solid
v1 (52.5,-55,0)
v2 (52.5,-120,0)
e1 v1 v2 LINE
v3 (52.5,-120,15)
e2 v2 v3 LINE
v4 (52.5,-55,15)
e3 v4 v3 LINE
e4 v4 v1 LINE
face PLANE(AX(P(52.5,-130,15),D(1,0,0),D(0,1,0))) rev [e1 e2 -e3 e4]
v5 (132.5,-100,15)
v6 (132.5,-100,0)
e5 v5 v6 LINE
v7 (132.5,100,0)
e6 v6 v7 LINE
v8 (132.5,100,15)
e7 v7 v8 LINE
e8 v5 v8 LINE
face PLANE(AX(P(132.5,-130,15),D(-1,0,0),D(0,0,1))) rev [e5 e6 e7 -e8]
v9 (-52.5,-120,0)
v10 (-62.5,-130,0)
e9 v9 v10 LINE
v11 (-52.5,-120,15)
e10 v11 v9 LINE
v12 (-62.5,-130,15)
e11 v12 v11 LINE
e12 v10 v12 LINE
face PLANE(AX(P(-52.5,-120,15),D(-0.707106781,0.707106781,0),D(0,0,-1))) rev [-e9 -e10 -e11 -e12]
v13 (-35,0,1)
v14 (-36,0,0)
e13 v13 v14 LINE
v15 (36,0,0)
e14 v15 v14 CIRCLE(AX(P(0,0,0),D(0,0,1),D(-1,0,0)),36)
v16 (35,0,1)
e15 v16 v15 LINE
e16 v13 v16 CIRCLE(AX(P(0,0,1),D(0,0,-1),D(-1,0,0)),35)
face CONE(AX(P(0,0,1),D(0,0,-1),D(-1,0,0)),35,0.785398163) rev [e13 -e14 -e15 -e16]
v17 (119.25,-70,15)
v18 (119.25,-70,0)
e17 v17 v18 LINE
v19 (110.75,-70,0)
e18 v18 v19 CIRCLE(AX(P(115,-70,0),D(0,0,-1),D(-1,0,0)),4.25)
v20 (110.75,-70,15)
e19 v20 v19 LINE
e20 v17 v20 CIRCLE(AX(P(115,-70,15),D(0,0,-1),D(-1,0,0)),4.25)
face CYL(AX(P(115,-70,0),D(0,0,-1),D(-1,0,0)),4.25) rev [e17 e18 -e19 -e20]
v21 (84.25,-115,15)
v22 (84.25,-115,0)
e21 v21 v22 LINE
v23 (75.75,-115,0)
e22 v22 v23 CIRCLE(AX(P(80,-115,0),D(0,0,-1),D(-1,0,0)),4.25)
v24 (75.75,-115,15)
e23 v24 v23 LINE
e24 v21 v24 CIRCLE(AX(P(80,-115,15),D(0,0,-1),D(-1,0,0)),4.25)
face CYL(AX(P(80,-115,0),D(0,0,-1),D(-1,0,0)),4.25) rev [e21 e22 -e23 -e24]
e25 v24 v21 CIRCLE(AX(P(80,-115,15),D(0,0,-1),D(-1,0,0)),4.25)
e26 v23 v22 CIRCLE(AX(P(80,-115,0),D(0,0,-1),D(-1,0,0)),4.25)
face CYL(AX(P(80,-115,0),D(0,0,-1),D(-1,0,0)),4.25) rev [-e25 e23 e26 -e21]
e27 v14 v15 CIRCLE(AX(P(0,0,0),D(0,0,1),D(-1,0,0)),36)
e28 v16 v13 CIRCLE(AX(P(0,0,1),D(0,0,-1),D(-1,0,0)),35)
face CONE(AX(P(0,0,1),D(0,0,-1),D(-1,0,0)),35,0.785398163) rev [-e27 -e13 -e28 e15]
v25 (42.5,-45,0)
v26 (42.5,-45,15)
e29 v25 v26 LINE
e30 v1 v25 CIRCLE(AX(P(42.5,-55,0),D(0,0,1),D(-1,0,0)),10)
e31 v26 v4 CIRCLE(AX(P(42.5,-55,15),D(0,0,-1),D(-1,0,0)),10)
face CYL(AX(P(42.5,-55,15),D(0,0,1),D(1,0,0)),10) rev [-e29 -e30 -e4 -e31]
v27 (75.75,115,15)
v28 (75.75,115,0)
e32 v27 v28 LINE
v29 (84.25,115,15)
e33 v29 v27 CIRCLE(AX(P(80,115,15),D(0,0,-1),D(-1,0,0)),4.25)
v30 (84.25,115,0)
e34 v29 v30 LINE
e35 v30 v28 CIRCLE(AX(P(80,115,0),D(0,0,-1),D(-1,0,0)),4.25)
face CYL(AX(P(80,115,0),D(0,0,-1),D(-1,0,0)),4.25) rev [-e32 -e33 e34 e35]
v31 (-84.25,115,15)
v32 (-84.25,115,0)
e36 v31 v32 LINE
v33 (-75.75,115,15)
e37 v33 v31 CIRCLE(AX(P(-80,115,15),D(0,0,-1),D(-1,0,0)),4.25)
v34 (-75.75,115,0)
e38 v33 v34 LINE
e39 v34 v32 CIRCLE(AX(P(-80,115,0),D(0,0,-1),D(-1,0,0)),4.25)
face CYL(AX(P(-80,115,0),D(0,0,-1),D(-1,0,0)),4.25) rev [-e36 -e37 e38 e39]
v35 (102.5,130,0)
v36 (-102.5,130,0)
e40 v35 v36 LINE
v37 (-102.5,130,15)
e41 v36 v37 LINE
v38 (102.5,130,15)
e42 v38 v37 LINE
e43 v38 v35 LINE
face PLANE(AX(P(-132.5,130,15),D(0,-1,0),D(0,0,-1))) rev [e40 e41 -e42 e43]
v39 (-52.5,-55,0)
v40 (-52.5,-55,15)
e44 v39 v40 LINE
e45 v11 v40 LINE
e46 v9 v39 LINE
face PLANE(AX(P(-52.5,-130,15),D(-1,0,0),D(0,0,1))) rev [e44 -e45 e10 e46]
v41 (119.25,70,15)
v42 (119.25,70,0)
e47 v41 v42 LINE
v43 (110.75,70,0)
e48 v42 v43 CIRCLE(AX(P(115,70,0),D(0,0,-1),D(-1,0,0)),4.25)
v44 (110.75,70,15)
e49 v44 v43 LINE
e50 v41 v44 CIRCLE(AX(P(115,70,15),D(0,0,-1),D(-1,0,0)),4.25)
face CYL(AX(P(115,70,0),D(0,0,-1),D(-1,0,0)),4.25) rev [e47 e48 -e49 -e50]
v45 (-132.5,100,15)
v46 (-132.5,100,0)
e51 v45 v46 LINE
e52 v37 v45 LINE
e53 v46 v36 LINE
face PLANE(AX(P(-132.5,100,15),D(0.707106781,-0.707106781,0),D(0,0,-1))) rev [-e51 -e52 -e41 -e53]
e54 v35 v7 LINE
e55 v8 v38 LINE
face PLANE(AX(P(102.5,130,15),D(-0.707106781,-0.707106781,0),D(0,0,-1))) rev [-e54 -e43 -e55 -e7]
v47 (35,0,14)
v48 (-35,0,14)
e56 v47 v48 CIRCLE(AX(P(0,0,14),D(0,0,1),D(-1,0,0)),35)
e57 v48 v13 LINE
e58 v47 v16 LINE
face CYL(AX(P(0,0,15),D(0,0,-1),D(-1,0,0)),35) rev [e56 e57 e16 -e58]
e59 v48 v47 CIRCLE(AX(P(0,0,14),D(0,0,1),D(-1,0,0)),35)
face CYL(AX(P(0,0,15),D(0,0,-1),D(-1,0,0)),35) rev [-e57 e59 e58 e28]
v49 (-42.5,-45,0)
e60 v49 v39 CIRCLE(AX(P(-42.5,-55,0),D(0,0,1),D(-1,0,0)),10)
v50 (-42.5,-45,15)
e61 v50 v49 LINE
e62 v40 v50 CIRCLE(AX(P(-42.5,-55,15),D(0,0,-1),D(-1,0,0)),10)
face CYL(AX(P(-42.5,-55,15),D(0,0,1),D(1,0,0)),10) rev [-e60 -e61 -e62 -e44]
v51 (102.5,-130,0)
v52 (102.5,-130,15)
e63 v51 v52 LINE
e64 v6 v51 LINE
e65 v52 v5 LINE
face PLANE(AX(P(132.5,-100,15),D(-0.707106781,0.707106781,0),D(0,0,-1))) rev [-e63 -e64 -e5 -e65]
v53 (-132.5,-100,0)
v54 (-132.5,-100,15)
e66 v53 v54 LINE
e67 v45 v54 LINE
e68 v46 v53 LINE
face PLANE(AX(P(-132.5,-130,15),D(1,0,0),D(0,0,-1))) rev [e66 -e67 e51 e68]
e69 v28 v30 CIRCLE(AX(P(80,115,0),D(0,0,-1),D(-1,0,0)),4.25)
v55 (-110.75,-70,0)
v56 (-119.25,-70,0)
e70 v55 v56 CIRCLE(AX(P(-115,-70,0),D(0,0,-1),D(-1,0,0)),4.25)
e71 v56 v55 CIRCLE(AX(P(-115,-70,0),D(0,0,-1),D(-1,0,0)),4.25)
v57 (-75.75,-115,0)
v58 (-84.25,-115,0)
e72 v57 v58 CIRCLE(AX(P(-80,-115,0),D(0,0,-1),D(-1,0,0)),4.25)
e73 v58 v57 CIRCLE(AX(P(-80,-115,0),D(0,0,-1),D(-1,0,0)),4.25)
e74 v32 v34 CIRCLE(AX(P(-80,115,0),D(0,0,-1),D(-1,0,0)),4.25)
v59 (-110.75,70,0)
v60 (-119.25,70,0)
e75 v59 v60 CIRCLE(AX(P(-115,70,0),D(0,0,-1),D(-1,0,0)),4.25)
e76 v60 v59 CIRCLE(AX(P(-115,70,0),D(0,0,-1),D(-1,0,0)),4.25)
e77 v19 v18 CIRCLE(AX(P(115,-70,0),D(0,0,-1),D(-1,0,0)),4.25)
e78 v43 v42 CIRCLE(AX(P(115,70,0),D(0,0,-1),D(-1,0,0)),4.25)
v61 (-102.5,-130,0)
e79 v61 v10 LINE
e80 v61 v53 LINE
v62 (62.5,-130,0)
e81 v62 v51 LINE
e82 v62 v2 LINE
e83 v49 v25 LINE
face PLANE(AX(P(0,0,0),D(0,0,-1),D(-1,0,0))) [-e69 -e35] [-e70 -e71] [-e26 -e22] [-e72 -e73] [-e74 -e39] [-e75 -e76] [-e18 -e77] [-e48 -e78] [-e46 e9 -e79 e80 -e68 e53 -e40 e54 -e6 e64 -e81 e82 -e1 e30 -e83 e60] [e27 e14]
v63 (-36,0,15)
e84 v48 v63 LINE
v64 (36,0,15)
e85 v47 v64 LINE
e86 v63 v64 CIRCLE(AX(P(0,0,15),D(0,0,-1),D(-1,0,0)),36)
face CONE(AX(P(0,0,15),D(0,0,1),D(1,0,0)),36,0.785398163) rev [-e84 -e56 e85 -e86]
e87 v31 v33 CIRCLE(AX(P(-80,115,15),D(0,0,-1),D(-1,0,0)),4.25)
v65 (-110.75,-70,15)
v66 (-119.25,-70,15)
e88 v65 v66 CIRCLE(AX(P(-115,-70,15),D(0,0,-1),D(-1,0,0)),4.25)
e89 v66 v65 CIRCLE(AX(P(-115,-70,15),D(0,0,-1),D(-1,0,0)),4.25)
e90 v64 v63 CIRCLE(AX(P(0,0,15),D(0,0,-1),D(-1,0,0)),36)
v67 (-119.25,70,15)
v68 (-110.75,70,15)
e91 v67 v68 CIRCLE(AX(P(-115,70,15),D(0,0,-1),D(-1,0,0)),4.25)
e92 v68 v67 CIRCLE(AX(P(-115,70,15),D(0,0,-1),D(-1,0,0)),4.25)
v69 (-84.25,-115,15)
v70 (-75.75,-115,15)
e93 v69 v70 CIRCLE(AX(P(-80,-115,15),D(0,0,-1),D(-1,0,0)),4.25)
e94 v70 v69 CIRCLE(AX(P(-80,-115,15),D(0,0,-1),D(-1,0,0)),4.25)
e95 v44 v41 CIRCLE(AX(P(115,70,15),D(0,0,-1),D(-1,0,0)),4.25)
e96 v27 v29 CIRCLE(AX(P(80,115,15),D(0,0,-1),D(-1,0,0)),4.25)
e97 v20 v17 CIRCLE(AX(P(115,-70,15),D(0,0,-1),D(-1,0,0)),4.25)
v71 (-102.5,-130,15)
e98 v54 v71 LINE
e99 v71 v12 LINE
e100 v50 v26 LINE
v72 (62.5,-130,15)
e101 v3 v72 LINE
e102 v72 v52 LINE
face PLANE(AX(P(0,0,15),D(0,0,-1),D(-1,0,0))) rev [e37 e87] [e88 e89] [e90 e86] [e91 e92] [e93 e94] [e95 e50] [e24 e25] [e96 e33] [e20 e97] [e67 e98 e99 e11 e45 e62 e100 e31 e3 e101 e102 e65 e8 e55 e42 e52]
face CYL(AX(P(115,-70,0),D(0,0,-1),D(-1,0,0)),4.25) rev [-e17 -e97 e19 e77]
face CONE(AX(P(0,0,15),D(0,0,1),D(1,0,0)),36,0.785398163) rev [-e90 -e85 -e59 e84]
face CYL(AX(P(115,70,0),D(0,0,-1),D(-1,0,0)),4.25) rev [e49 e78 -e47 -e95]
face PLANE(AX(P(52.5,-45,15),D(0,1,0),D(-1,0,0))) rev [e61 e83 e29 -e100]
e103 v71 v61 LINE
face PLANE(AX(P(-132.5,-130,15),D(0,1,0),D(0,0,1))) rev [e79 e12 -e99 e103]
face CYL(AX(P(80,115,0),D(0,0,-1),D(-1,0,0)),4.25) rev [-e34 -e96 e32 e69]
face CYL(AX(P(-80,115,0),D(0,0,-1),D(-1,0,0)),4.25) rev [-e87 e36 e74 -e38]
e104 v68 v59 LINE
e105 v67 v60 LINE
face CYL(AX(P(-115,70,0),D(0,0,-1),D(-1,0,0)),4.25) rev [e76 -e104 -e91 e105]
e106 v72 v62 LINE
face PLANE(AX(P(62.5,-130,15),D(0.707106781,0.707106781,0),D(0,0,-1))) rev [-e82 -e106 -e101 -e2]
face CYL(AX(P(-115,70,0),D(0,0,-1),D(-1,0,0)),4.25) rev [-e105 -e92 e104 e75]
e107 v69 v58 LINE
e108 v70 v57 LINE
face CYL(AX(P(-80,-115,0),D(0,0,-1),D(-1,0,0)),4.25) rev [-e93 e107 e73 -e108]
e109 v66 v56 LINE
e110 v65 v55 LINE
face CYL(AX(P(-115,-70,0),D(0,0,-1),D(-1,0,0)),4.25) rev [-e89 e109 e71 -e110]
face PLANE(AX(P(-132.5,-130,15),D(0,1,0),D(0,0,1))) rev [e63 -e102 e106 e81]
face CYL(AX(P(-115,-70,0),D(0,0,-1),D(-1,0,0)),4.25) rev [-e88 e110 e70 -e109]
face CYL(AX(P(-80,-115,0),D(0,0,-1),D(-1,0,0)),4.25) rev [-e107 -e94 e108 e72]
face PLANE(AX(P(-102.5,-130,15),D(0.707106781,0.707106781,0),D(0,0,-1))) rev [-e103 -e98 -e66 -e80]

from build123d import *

# Parameters (mm, degrees)
SKETCH_1_W          = 265
SKETCH_1_H          = 260
EXTRUDE_1_DEPTH     = 15
HOLE_WIZARD_M10_1_D = 8.5
SKETCH_4_W          = 105
SKETCH_4_H          = 85
CUT_EXTRUDE_1_DEPTH = 187.229025665
FILLET_1_R          = 10
SKETCH_5_R          = 35
CUT_EXTRUDE_2_DEPTH = 187.229025665
CHAMFER_2_SIZE      = 1
CHAMFER_1_SIZE      = 30
CHAMFER_3_SIZE      = 10


with BuildPart() as part:
    # 草图1 → 凸台-拉伸1 (new body)
    with BuildSketch(Plane.XY):
        Rectangle(SKETCH_1_W, SKETCH_1_H)
    extrude(amount=EXTRUDE_1_DEPTH)

    # M10 螺纹孔1 (through all)
    with Locations(Plane(origin=(0, 0, 0), x_dir=(-1, 0, 0), z_dir=(0, 0, -1))):
        with Locations((-80, 115), (-115, 70), (-115, -70), (-80, -115), (80, -115), (115, -70), (115, 70), (80, 115)):
            Hole(HOLE_WIZARD_M10_1_D / 2)

    # 草图4 → 切除-拉伸1 (cut, through all)
    with BuildSketch(Plane(origin=(0, 0, 0), x_dir=(-1, 0, 0), z_dir=(0, 0, -1))):
        with Locations((0, -87.5)):
            Rectangle(SKETCH_4_W, SKETCH_4_H)
    extrude(amount=-CUT_EXTRUDE_1_DEPTH, mode=Mode.SUBTRACT)

    # 圆角1
    fillet_1_edges = [part.edges().sort_by_distance(p)[0] for p in [
        (52.5, -45, 7.5),
        (-52.5, -45, 7.5),
    ]]
    fillet(fillet_1_edges, radius=FILLET_1_R)

    # 草图5 → 切除-拉伸2 (cut, through all)
    with BuildSketch(Plane(origin=(0, 0, 0), x_dir=(-1, 0, 0), z_dir=(0, 0, -1))):
        Circle(SKETCH_5_R)
    extrude(amount=-CUT_EXTRUDE_2_DEPTH, mode=Mode.SUBTRACT)

    # 倒角2
    chamfer_2_edges = [part.edges().sort_by_distance(p)[0] for p in [
        (35, 0, 15),
        (35, 0, 0),
    ]]
    chamfer(chamfer_2_edges, length=CHAMFER_2_SIZE)

    # 倒角1
    chamfer_1_edges = [part.edges().sort_by_distance(p)[0] for p in [
        (132.5, -130, 7.5),
        (-132.5, -130, 7.5),
        (-132.5, 130, 7.5),
        (132.5, 130, 7.5),
    ]]
    chamfer(chamfer_1_edges, length=CHAMFER_1_SIZE)

    # 倒角3
    chamfer_3_edges = [part.edges().sort_by_distance(p)[0] for p in [
        (52.5, -130, 7.5),
        (-52.5, -130, 7.5),
    ]]
    chamfer(chamfer_3_edges, length=CHAMFER_3_SIZE)


solid = part.part
